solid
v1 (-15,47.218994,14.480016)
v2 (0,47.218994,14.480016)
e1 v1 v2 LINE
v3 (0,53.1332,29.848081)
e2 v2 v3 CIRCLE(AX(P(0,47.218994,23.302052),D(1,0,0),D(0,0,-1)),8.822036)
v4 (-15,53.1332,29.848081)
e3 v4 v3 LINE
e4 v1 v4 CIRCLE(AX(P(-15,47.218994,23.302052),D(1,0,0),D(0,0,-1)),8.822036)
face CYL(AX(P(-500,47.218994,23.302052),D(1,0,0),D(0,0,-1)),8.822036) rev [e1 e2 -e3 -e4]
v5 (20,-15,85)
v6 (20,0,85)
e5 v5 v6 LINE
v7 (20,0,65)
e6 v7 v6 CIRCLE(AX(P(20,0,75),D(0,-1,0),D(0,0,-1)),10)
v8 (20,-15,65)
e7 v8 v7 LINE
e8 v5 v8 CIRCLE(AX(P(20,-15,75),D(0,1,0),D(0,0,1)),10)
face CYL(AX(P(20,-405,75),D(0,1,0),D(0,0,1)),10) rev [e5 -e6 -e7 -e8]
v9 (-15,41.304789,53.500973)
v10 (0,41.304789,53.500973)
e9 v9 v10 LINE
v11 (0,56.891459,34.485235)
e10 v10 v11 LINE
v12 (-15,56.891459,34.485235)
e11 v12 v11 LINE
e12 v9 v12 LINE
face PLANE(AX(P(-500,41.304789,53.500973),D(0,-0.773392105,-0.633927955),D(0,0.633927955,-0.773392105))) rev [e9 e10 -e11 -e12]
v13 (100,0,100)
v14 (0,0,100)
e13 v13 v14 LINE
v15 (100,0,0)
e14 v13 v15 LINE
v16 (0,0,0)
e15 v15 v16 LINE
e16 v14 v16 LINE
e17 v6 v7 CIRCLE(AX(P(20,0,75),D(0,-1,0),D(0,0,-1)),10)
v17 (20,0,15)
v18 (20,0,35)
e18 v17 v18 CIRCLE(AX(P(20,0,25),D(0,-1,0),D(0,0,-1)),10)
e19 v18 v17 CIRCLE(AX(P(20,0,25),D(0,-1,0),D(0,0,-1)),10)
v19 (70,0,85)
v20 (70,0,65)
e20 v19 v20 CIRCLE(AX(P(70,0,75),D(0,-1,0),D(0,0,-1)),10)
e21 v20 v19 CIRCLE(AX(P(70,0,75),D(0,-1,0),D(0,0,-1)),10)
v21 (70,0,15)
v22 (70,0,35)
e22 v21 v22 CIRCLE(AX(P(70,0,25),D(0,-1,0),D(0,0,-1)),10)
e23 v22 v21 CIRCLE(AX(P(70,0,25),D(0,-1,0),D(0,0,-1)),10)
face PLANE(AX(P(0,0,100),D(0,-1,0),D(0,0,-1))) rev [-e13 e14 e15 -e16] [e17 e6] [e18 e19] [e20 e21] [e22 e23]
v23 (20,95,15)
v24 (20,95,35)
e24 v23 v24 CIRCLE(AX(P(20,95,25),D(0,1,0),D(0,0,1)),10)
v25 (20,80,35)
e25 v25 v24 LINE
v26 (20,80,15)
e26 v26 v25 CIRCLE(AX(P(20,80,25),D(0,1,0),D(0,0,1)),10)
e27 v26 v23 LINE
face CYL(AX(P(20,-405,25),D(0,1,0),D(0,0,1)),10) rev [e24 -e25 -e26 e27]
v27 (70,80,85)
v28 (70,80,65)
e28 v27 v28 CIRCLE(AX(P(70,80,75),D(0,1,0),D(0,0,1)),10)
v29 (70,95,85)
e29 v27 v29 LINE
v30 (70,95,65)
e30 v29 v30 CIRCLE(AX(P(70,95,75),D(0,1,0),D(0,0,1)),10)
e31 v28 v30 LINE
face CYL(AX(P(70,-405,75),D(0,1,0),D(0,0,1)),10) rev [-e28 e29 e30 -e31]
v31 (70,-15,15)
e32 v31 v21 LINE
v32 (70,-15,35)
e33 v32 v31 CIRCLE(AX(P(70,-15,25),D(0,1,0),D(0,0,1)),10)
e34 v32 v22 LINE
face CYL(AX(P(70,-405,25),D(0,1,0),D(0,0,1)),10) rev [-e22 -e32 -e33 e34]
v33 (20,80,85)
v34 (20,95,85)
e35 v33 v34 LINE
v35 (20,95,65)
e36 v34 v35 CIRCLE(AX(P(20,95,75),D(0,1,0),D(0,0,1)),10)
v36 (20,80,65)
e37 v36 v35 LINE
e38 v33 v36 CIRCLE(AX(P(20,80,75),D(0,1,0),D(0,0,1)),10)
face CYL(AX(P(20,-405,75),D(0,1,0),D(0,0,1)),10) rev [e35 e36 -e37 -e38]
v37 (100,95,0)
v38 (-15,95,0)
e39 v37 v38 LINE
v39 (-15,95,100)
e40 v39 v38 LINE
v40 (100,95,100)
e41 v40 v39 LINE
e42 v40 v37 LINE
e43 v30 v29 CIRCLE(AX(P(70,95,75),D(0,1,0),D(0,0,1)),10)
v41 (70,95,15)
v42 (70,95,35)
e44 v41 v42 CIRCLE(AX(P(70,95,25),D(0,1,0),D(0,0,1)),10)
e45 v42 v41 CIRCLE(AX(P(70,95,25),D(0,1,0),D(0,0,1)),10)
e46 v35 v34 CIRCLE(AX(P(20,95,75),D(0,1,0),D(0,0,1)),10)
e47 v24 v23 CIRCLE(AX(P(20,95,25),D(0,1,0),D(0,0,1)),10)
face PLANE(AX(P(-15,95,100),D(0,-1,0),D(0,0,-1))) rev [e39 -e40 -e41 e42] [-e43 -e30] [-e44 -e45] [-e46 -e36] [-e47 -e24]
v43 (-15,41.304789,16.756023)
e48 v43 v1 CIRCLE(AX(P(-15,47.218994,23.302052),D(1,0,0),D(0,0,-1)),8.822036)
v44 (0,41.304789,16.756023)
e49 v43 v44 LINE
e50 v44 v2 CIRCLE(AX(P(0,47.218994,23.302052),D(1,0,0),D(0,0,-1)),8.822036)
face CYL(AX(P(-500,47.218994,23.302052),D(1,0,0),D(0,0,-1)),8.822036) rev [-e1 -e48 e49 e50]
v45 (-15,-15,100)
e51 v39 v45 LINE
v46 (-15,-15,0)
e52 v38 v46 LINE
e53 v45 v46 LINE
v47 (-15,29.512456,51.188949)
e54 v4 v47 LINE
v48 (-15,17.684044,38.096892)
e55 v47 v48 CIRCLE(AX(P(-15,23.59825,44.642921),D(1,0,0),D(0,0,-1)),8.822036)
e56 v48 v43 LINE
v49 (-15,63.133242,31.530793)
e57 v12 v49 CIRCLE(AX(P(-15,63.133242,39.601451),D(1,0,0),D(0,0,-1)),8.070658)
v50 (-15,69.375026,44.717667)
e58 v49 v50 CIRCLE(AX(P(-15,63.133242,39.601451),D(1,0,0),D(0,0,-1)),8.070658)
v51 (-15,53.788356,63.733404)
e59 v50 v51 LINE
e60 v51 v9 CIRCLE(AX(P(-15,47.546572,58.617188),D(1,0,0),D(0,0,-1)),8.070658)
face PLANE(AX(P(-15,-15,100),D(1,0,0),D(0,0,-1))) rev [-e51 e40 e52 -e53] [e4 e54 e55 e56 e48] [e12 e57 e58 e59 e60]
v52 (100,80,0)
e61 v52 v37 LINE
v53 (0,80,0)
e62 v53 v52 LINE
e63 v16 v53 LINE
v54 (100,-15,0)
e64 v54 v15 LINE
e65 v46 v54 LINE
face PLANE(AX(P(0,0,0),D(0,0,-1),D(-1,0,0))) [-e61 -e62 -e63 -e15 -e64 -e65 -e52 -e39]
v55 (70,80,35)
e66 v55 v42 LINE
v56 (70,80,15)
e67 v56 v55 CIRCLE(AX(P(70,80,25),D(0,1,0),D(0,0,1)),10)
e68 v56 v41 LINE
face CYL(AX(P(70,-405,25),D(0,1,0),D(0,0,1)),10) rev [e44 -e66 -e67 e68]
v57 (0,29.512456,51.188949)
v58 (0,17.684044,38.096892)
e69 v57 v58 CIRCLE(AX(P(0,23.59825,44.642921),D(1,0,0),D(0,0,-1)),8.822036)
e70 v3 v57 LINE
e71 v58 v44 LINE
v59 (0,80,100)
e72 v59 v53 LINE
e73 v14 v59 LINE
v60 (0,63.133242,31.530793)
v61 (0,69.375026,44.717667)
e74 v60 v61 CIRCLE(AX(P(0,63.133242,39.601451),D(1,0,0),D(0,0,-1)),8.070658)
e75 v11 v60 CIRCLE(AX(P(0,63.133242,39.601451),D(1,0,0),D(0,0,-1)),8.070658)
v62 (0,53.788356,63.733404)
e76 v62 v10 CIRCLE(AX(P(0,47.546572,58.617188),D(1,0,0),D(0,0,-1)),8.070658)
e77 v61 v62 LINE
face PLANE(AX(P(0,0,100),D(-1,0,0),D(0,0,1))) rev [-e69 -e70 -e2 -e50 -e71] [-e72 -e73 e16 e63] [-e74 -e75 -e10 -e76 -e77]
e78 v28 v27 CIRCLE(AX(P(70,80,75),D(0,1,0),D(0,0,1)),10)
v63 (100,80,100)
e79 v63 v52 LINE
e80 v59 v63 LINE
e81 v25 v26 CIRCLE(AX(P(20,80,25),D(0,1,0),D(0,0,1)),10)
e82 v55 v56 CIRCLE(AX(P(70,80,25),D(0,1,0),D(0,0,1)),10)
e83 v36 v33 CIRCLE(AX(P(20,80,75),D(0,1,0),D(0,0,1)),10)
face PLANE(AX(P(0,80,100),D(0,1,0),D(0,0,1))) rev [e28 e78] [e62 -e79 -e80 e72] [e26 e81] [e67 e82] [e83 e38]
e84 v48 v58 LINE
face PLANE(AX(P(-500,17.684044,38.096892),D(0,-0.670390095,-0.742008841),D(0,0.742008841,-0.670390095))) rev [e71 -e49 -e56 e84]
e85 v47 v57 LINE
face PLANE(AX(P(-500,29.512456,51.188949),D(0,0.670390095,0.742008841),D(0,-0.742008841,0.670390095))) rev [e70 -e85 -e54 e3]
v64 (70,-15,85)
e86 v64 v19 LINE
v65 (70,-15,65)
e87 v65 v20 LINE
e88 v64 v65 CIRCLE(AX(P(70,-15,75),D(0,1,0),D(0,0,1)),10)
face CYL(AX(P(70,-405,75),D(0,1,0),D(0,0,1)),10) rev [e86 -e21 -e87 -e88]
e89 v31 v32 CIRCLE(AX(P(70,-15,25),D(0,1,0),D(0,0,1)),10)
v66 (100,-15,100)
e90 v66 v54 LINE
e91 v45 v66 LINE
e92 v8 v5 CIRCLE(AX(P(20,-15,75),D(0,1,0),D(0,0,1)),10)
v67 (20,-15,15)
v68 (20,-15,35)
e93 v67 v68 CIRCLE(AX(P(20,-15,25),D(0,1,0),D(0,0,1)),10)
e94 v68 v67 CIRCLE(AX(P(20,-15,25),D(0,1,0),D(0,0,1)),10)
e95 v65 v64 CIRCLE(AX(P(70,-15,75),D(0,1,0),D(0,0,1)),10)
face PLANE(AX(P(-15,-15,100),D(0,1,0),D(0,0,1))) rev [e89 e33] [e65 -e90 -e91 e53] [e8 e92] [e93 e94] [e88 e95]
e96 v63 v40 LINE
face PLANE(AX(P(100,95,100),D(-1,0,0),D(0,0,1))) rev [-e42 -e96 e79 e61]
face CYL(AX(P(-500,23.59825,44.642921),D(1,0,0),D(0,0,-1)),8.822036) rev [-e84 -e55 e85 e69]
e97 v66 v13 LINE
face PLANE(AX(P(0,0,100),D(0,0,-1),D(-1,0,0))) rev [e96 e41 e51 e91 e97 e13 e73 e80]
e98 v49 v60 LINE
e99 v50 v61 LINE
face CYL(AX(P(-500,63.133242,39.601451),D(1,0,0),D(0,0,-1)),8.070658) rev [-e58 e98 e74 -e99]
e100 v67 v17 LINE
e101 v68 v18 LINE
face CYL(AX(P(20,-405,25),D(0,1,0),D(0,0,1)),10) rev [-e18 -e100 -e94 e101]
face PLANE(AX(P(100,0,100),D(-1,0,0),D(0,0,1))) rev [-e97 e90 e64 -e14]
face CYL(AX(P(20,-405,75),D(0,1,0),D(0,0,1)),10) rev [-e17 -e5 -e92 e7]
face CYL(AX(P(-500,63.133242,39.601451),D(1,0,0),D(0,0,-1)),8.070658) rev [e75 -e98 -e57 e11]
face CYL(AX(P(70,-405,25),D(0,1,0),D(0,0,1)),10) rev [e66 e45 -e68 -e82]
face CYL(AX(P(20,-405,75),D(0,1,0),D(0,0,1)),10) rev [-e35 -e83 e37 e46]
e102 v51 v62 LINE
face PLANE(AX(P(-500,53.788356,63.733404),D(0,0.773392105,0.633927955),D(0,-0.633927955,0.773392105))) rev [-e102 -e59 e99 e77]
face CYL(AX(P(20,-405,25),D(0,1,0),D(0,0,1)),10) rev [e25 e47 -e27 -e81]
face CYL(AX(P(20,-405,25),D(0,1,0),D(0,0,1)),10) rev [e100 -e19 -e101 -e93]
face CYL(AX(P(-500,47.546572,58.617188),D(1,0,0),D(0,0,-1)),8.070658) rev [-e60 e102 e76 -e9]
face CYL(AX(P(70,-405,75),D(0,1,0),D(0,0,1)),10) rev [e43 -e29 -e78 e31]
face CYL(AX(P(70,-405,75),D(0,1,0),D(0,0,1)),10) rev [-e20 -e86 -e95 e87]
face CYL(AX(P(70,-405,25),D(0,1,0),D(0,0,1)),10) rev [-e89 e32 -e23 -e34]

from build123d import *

# Parameters (mm, degrees)
BOSS_EXTRUDE1_DEPTH = 100
SKETCH2_R           = 10
CUT_EXTRUDE1_DEPTH  = 500
CUT_EXTRUDE2_DEPTH  = 500


with BuildPart() as part:
    # Sketch1 → Boss-Extrude1 (new body)
    with BuildSketch(Plane.XY):
        Polygon((0, 0), (100, 0), (100, -15), (-15, -15), (-15, 95), (100, 95), (100, 80), (0, 80), align=None)
    extrude(amount=BOSS_EXTRUDE1_DEPTH)

    # Sketch2 → Cut-Extrude1 (cut)
    with BuildSketch(Plane(origin=(0, 95, 0), x_dir=(1, 0, 0), z_dir=(0, 1, 0))):
        with Locations(Location((20, -25, 0), (0, 0, 270))):
            Circle(SKETCH2_R)
        with Locations(Location((70, -25, 0), (0, 0, 270))):
            Circle(SKETCH2_R)
        with Locations(Location((20, -75, 0), (0, 0, 270))):
            Circle(SKETCH2_R)
        with Locations(Location((70, -75, 0), (0, 0, 270))):
            Circle(SKETCH2_R)
    extrude(amount=-CUT_EXTRUDE1_DEPTH, mode=Mode.SUBTRACT)

    # Sketch3 → Cut-Extrude2 (cut)
    with BuildSketch(Plane(origin=(0, 0, 0), x_dir=(0, 0, -1), z_dir=(1, 0, 0))):
        with BuildLine():
            Line((-63.733404472, 53.788355895), (-44.717667379, 69.375025643))
            ThreePointArc((-44.717667379, 69.375025643), (-33.359667898, 68.249458127), (-34.485235414, 56.891458646))
            Line((-34.485235414, 56.891458646), (-53.500972507, 41.304788898))
            ThreePointArc((-53.500972507, 41.304788898), (-64.858971988, 42.430356414), (-63.733404472, 53.788355895))
        make_face()
        with BuildLine():
            Line((-51.188949328, 29.512455593), (-29.848080815, 53.133200052))
            ThreePointArc((-29.848080815, 53.133200052), (-17.387846498, 53.765023215), (-16.756023336, 41.304788898))
            Line((-16.756023336, 41.304788898), (-38.096891848, 17.684044439))
            ThreePointArc((-38.096891848, 17.684044439), (-50.557126165, 17.052221277), (-51.188949328, 29.512455593))
        make_face()
    extrude(amount=-CUT_EXTRUDE2_DEPTH, mode=Mode.SUBTRACT)


solid = part.part
